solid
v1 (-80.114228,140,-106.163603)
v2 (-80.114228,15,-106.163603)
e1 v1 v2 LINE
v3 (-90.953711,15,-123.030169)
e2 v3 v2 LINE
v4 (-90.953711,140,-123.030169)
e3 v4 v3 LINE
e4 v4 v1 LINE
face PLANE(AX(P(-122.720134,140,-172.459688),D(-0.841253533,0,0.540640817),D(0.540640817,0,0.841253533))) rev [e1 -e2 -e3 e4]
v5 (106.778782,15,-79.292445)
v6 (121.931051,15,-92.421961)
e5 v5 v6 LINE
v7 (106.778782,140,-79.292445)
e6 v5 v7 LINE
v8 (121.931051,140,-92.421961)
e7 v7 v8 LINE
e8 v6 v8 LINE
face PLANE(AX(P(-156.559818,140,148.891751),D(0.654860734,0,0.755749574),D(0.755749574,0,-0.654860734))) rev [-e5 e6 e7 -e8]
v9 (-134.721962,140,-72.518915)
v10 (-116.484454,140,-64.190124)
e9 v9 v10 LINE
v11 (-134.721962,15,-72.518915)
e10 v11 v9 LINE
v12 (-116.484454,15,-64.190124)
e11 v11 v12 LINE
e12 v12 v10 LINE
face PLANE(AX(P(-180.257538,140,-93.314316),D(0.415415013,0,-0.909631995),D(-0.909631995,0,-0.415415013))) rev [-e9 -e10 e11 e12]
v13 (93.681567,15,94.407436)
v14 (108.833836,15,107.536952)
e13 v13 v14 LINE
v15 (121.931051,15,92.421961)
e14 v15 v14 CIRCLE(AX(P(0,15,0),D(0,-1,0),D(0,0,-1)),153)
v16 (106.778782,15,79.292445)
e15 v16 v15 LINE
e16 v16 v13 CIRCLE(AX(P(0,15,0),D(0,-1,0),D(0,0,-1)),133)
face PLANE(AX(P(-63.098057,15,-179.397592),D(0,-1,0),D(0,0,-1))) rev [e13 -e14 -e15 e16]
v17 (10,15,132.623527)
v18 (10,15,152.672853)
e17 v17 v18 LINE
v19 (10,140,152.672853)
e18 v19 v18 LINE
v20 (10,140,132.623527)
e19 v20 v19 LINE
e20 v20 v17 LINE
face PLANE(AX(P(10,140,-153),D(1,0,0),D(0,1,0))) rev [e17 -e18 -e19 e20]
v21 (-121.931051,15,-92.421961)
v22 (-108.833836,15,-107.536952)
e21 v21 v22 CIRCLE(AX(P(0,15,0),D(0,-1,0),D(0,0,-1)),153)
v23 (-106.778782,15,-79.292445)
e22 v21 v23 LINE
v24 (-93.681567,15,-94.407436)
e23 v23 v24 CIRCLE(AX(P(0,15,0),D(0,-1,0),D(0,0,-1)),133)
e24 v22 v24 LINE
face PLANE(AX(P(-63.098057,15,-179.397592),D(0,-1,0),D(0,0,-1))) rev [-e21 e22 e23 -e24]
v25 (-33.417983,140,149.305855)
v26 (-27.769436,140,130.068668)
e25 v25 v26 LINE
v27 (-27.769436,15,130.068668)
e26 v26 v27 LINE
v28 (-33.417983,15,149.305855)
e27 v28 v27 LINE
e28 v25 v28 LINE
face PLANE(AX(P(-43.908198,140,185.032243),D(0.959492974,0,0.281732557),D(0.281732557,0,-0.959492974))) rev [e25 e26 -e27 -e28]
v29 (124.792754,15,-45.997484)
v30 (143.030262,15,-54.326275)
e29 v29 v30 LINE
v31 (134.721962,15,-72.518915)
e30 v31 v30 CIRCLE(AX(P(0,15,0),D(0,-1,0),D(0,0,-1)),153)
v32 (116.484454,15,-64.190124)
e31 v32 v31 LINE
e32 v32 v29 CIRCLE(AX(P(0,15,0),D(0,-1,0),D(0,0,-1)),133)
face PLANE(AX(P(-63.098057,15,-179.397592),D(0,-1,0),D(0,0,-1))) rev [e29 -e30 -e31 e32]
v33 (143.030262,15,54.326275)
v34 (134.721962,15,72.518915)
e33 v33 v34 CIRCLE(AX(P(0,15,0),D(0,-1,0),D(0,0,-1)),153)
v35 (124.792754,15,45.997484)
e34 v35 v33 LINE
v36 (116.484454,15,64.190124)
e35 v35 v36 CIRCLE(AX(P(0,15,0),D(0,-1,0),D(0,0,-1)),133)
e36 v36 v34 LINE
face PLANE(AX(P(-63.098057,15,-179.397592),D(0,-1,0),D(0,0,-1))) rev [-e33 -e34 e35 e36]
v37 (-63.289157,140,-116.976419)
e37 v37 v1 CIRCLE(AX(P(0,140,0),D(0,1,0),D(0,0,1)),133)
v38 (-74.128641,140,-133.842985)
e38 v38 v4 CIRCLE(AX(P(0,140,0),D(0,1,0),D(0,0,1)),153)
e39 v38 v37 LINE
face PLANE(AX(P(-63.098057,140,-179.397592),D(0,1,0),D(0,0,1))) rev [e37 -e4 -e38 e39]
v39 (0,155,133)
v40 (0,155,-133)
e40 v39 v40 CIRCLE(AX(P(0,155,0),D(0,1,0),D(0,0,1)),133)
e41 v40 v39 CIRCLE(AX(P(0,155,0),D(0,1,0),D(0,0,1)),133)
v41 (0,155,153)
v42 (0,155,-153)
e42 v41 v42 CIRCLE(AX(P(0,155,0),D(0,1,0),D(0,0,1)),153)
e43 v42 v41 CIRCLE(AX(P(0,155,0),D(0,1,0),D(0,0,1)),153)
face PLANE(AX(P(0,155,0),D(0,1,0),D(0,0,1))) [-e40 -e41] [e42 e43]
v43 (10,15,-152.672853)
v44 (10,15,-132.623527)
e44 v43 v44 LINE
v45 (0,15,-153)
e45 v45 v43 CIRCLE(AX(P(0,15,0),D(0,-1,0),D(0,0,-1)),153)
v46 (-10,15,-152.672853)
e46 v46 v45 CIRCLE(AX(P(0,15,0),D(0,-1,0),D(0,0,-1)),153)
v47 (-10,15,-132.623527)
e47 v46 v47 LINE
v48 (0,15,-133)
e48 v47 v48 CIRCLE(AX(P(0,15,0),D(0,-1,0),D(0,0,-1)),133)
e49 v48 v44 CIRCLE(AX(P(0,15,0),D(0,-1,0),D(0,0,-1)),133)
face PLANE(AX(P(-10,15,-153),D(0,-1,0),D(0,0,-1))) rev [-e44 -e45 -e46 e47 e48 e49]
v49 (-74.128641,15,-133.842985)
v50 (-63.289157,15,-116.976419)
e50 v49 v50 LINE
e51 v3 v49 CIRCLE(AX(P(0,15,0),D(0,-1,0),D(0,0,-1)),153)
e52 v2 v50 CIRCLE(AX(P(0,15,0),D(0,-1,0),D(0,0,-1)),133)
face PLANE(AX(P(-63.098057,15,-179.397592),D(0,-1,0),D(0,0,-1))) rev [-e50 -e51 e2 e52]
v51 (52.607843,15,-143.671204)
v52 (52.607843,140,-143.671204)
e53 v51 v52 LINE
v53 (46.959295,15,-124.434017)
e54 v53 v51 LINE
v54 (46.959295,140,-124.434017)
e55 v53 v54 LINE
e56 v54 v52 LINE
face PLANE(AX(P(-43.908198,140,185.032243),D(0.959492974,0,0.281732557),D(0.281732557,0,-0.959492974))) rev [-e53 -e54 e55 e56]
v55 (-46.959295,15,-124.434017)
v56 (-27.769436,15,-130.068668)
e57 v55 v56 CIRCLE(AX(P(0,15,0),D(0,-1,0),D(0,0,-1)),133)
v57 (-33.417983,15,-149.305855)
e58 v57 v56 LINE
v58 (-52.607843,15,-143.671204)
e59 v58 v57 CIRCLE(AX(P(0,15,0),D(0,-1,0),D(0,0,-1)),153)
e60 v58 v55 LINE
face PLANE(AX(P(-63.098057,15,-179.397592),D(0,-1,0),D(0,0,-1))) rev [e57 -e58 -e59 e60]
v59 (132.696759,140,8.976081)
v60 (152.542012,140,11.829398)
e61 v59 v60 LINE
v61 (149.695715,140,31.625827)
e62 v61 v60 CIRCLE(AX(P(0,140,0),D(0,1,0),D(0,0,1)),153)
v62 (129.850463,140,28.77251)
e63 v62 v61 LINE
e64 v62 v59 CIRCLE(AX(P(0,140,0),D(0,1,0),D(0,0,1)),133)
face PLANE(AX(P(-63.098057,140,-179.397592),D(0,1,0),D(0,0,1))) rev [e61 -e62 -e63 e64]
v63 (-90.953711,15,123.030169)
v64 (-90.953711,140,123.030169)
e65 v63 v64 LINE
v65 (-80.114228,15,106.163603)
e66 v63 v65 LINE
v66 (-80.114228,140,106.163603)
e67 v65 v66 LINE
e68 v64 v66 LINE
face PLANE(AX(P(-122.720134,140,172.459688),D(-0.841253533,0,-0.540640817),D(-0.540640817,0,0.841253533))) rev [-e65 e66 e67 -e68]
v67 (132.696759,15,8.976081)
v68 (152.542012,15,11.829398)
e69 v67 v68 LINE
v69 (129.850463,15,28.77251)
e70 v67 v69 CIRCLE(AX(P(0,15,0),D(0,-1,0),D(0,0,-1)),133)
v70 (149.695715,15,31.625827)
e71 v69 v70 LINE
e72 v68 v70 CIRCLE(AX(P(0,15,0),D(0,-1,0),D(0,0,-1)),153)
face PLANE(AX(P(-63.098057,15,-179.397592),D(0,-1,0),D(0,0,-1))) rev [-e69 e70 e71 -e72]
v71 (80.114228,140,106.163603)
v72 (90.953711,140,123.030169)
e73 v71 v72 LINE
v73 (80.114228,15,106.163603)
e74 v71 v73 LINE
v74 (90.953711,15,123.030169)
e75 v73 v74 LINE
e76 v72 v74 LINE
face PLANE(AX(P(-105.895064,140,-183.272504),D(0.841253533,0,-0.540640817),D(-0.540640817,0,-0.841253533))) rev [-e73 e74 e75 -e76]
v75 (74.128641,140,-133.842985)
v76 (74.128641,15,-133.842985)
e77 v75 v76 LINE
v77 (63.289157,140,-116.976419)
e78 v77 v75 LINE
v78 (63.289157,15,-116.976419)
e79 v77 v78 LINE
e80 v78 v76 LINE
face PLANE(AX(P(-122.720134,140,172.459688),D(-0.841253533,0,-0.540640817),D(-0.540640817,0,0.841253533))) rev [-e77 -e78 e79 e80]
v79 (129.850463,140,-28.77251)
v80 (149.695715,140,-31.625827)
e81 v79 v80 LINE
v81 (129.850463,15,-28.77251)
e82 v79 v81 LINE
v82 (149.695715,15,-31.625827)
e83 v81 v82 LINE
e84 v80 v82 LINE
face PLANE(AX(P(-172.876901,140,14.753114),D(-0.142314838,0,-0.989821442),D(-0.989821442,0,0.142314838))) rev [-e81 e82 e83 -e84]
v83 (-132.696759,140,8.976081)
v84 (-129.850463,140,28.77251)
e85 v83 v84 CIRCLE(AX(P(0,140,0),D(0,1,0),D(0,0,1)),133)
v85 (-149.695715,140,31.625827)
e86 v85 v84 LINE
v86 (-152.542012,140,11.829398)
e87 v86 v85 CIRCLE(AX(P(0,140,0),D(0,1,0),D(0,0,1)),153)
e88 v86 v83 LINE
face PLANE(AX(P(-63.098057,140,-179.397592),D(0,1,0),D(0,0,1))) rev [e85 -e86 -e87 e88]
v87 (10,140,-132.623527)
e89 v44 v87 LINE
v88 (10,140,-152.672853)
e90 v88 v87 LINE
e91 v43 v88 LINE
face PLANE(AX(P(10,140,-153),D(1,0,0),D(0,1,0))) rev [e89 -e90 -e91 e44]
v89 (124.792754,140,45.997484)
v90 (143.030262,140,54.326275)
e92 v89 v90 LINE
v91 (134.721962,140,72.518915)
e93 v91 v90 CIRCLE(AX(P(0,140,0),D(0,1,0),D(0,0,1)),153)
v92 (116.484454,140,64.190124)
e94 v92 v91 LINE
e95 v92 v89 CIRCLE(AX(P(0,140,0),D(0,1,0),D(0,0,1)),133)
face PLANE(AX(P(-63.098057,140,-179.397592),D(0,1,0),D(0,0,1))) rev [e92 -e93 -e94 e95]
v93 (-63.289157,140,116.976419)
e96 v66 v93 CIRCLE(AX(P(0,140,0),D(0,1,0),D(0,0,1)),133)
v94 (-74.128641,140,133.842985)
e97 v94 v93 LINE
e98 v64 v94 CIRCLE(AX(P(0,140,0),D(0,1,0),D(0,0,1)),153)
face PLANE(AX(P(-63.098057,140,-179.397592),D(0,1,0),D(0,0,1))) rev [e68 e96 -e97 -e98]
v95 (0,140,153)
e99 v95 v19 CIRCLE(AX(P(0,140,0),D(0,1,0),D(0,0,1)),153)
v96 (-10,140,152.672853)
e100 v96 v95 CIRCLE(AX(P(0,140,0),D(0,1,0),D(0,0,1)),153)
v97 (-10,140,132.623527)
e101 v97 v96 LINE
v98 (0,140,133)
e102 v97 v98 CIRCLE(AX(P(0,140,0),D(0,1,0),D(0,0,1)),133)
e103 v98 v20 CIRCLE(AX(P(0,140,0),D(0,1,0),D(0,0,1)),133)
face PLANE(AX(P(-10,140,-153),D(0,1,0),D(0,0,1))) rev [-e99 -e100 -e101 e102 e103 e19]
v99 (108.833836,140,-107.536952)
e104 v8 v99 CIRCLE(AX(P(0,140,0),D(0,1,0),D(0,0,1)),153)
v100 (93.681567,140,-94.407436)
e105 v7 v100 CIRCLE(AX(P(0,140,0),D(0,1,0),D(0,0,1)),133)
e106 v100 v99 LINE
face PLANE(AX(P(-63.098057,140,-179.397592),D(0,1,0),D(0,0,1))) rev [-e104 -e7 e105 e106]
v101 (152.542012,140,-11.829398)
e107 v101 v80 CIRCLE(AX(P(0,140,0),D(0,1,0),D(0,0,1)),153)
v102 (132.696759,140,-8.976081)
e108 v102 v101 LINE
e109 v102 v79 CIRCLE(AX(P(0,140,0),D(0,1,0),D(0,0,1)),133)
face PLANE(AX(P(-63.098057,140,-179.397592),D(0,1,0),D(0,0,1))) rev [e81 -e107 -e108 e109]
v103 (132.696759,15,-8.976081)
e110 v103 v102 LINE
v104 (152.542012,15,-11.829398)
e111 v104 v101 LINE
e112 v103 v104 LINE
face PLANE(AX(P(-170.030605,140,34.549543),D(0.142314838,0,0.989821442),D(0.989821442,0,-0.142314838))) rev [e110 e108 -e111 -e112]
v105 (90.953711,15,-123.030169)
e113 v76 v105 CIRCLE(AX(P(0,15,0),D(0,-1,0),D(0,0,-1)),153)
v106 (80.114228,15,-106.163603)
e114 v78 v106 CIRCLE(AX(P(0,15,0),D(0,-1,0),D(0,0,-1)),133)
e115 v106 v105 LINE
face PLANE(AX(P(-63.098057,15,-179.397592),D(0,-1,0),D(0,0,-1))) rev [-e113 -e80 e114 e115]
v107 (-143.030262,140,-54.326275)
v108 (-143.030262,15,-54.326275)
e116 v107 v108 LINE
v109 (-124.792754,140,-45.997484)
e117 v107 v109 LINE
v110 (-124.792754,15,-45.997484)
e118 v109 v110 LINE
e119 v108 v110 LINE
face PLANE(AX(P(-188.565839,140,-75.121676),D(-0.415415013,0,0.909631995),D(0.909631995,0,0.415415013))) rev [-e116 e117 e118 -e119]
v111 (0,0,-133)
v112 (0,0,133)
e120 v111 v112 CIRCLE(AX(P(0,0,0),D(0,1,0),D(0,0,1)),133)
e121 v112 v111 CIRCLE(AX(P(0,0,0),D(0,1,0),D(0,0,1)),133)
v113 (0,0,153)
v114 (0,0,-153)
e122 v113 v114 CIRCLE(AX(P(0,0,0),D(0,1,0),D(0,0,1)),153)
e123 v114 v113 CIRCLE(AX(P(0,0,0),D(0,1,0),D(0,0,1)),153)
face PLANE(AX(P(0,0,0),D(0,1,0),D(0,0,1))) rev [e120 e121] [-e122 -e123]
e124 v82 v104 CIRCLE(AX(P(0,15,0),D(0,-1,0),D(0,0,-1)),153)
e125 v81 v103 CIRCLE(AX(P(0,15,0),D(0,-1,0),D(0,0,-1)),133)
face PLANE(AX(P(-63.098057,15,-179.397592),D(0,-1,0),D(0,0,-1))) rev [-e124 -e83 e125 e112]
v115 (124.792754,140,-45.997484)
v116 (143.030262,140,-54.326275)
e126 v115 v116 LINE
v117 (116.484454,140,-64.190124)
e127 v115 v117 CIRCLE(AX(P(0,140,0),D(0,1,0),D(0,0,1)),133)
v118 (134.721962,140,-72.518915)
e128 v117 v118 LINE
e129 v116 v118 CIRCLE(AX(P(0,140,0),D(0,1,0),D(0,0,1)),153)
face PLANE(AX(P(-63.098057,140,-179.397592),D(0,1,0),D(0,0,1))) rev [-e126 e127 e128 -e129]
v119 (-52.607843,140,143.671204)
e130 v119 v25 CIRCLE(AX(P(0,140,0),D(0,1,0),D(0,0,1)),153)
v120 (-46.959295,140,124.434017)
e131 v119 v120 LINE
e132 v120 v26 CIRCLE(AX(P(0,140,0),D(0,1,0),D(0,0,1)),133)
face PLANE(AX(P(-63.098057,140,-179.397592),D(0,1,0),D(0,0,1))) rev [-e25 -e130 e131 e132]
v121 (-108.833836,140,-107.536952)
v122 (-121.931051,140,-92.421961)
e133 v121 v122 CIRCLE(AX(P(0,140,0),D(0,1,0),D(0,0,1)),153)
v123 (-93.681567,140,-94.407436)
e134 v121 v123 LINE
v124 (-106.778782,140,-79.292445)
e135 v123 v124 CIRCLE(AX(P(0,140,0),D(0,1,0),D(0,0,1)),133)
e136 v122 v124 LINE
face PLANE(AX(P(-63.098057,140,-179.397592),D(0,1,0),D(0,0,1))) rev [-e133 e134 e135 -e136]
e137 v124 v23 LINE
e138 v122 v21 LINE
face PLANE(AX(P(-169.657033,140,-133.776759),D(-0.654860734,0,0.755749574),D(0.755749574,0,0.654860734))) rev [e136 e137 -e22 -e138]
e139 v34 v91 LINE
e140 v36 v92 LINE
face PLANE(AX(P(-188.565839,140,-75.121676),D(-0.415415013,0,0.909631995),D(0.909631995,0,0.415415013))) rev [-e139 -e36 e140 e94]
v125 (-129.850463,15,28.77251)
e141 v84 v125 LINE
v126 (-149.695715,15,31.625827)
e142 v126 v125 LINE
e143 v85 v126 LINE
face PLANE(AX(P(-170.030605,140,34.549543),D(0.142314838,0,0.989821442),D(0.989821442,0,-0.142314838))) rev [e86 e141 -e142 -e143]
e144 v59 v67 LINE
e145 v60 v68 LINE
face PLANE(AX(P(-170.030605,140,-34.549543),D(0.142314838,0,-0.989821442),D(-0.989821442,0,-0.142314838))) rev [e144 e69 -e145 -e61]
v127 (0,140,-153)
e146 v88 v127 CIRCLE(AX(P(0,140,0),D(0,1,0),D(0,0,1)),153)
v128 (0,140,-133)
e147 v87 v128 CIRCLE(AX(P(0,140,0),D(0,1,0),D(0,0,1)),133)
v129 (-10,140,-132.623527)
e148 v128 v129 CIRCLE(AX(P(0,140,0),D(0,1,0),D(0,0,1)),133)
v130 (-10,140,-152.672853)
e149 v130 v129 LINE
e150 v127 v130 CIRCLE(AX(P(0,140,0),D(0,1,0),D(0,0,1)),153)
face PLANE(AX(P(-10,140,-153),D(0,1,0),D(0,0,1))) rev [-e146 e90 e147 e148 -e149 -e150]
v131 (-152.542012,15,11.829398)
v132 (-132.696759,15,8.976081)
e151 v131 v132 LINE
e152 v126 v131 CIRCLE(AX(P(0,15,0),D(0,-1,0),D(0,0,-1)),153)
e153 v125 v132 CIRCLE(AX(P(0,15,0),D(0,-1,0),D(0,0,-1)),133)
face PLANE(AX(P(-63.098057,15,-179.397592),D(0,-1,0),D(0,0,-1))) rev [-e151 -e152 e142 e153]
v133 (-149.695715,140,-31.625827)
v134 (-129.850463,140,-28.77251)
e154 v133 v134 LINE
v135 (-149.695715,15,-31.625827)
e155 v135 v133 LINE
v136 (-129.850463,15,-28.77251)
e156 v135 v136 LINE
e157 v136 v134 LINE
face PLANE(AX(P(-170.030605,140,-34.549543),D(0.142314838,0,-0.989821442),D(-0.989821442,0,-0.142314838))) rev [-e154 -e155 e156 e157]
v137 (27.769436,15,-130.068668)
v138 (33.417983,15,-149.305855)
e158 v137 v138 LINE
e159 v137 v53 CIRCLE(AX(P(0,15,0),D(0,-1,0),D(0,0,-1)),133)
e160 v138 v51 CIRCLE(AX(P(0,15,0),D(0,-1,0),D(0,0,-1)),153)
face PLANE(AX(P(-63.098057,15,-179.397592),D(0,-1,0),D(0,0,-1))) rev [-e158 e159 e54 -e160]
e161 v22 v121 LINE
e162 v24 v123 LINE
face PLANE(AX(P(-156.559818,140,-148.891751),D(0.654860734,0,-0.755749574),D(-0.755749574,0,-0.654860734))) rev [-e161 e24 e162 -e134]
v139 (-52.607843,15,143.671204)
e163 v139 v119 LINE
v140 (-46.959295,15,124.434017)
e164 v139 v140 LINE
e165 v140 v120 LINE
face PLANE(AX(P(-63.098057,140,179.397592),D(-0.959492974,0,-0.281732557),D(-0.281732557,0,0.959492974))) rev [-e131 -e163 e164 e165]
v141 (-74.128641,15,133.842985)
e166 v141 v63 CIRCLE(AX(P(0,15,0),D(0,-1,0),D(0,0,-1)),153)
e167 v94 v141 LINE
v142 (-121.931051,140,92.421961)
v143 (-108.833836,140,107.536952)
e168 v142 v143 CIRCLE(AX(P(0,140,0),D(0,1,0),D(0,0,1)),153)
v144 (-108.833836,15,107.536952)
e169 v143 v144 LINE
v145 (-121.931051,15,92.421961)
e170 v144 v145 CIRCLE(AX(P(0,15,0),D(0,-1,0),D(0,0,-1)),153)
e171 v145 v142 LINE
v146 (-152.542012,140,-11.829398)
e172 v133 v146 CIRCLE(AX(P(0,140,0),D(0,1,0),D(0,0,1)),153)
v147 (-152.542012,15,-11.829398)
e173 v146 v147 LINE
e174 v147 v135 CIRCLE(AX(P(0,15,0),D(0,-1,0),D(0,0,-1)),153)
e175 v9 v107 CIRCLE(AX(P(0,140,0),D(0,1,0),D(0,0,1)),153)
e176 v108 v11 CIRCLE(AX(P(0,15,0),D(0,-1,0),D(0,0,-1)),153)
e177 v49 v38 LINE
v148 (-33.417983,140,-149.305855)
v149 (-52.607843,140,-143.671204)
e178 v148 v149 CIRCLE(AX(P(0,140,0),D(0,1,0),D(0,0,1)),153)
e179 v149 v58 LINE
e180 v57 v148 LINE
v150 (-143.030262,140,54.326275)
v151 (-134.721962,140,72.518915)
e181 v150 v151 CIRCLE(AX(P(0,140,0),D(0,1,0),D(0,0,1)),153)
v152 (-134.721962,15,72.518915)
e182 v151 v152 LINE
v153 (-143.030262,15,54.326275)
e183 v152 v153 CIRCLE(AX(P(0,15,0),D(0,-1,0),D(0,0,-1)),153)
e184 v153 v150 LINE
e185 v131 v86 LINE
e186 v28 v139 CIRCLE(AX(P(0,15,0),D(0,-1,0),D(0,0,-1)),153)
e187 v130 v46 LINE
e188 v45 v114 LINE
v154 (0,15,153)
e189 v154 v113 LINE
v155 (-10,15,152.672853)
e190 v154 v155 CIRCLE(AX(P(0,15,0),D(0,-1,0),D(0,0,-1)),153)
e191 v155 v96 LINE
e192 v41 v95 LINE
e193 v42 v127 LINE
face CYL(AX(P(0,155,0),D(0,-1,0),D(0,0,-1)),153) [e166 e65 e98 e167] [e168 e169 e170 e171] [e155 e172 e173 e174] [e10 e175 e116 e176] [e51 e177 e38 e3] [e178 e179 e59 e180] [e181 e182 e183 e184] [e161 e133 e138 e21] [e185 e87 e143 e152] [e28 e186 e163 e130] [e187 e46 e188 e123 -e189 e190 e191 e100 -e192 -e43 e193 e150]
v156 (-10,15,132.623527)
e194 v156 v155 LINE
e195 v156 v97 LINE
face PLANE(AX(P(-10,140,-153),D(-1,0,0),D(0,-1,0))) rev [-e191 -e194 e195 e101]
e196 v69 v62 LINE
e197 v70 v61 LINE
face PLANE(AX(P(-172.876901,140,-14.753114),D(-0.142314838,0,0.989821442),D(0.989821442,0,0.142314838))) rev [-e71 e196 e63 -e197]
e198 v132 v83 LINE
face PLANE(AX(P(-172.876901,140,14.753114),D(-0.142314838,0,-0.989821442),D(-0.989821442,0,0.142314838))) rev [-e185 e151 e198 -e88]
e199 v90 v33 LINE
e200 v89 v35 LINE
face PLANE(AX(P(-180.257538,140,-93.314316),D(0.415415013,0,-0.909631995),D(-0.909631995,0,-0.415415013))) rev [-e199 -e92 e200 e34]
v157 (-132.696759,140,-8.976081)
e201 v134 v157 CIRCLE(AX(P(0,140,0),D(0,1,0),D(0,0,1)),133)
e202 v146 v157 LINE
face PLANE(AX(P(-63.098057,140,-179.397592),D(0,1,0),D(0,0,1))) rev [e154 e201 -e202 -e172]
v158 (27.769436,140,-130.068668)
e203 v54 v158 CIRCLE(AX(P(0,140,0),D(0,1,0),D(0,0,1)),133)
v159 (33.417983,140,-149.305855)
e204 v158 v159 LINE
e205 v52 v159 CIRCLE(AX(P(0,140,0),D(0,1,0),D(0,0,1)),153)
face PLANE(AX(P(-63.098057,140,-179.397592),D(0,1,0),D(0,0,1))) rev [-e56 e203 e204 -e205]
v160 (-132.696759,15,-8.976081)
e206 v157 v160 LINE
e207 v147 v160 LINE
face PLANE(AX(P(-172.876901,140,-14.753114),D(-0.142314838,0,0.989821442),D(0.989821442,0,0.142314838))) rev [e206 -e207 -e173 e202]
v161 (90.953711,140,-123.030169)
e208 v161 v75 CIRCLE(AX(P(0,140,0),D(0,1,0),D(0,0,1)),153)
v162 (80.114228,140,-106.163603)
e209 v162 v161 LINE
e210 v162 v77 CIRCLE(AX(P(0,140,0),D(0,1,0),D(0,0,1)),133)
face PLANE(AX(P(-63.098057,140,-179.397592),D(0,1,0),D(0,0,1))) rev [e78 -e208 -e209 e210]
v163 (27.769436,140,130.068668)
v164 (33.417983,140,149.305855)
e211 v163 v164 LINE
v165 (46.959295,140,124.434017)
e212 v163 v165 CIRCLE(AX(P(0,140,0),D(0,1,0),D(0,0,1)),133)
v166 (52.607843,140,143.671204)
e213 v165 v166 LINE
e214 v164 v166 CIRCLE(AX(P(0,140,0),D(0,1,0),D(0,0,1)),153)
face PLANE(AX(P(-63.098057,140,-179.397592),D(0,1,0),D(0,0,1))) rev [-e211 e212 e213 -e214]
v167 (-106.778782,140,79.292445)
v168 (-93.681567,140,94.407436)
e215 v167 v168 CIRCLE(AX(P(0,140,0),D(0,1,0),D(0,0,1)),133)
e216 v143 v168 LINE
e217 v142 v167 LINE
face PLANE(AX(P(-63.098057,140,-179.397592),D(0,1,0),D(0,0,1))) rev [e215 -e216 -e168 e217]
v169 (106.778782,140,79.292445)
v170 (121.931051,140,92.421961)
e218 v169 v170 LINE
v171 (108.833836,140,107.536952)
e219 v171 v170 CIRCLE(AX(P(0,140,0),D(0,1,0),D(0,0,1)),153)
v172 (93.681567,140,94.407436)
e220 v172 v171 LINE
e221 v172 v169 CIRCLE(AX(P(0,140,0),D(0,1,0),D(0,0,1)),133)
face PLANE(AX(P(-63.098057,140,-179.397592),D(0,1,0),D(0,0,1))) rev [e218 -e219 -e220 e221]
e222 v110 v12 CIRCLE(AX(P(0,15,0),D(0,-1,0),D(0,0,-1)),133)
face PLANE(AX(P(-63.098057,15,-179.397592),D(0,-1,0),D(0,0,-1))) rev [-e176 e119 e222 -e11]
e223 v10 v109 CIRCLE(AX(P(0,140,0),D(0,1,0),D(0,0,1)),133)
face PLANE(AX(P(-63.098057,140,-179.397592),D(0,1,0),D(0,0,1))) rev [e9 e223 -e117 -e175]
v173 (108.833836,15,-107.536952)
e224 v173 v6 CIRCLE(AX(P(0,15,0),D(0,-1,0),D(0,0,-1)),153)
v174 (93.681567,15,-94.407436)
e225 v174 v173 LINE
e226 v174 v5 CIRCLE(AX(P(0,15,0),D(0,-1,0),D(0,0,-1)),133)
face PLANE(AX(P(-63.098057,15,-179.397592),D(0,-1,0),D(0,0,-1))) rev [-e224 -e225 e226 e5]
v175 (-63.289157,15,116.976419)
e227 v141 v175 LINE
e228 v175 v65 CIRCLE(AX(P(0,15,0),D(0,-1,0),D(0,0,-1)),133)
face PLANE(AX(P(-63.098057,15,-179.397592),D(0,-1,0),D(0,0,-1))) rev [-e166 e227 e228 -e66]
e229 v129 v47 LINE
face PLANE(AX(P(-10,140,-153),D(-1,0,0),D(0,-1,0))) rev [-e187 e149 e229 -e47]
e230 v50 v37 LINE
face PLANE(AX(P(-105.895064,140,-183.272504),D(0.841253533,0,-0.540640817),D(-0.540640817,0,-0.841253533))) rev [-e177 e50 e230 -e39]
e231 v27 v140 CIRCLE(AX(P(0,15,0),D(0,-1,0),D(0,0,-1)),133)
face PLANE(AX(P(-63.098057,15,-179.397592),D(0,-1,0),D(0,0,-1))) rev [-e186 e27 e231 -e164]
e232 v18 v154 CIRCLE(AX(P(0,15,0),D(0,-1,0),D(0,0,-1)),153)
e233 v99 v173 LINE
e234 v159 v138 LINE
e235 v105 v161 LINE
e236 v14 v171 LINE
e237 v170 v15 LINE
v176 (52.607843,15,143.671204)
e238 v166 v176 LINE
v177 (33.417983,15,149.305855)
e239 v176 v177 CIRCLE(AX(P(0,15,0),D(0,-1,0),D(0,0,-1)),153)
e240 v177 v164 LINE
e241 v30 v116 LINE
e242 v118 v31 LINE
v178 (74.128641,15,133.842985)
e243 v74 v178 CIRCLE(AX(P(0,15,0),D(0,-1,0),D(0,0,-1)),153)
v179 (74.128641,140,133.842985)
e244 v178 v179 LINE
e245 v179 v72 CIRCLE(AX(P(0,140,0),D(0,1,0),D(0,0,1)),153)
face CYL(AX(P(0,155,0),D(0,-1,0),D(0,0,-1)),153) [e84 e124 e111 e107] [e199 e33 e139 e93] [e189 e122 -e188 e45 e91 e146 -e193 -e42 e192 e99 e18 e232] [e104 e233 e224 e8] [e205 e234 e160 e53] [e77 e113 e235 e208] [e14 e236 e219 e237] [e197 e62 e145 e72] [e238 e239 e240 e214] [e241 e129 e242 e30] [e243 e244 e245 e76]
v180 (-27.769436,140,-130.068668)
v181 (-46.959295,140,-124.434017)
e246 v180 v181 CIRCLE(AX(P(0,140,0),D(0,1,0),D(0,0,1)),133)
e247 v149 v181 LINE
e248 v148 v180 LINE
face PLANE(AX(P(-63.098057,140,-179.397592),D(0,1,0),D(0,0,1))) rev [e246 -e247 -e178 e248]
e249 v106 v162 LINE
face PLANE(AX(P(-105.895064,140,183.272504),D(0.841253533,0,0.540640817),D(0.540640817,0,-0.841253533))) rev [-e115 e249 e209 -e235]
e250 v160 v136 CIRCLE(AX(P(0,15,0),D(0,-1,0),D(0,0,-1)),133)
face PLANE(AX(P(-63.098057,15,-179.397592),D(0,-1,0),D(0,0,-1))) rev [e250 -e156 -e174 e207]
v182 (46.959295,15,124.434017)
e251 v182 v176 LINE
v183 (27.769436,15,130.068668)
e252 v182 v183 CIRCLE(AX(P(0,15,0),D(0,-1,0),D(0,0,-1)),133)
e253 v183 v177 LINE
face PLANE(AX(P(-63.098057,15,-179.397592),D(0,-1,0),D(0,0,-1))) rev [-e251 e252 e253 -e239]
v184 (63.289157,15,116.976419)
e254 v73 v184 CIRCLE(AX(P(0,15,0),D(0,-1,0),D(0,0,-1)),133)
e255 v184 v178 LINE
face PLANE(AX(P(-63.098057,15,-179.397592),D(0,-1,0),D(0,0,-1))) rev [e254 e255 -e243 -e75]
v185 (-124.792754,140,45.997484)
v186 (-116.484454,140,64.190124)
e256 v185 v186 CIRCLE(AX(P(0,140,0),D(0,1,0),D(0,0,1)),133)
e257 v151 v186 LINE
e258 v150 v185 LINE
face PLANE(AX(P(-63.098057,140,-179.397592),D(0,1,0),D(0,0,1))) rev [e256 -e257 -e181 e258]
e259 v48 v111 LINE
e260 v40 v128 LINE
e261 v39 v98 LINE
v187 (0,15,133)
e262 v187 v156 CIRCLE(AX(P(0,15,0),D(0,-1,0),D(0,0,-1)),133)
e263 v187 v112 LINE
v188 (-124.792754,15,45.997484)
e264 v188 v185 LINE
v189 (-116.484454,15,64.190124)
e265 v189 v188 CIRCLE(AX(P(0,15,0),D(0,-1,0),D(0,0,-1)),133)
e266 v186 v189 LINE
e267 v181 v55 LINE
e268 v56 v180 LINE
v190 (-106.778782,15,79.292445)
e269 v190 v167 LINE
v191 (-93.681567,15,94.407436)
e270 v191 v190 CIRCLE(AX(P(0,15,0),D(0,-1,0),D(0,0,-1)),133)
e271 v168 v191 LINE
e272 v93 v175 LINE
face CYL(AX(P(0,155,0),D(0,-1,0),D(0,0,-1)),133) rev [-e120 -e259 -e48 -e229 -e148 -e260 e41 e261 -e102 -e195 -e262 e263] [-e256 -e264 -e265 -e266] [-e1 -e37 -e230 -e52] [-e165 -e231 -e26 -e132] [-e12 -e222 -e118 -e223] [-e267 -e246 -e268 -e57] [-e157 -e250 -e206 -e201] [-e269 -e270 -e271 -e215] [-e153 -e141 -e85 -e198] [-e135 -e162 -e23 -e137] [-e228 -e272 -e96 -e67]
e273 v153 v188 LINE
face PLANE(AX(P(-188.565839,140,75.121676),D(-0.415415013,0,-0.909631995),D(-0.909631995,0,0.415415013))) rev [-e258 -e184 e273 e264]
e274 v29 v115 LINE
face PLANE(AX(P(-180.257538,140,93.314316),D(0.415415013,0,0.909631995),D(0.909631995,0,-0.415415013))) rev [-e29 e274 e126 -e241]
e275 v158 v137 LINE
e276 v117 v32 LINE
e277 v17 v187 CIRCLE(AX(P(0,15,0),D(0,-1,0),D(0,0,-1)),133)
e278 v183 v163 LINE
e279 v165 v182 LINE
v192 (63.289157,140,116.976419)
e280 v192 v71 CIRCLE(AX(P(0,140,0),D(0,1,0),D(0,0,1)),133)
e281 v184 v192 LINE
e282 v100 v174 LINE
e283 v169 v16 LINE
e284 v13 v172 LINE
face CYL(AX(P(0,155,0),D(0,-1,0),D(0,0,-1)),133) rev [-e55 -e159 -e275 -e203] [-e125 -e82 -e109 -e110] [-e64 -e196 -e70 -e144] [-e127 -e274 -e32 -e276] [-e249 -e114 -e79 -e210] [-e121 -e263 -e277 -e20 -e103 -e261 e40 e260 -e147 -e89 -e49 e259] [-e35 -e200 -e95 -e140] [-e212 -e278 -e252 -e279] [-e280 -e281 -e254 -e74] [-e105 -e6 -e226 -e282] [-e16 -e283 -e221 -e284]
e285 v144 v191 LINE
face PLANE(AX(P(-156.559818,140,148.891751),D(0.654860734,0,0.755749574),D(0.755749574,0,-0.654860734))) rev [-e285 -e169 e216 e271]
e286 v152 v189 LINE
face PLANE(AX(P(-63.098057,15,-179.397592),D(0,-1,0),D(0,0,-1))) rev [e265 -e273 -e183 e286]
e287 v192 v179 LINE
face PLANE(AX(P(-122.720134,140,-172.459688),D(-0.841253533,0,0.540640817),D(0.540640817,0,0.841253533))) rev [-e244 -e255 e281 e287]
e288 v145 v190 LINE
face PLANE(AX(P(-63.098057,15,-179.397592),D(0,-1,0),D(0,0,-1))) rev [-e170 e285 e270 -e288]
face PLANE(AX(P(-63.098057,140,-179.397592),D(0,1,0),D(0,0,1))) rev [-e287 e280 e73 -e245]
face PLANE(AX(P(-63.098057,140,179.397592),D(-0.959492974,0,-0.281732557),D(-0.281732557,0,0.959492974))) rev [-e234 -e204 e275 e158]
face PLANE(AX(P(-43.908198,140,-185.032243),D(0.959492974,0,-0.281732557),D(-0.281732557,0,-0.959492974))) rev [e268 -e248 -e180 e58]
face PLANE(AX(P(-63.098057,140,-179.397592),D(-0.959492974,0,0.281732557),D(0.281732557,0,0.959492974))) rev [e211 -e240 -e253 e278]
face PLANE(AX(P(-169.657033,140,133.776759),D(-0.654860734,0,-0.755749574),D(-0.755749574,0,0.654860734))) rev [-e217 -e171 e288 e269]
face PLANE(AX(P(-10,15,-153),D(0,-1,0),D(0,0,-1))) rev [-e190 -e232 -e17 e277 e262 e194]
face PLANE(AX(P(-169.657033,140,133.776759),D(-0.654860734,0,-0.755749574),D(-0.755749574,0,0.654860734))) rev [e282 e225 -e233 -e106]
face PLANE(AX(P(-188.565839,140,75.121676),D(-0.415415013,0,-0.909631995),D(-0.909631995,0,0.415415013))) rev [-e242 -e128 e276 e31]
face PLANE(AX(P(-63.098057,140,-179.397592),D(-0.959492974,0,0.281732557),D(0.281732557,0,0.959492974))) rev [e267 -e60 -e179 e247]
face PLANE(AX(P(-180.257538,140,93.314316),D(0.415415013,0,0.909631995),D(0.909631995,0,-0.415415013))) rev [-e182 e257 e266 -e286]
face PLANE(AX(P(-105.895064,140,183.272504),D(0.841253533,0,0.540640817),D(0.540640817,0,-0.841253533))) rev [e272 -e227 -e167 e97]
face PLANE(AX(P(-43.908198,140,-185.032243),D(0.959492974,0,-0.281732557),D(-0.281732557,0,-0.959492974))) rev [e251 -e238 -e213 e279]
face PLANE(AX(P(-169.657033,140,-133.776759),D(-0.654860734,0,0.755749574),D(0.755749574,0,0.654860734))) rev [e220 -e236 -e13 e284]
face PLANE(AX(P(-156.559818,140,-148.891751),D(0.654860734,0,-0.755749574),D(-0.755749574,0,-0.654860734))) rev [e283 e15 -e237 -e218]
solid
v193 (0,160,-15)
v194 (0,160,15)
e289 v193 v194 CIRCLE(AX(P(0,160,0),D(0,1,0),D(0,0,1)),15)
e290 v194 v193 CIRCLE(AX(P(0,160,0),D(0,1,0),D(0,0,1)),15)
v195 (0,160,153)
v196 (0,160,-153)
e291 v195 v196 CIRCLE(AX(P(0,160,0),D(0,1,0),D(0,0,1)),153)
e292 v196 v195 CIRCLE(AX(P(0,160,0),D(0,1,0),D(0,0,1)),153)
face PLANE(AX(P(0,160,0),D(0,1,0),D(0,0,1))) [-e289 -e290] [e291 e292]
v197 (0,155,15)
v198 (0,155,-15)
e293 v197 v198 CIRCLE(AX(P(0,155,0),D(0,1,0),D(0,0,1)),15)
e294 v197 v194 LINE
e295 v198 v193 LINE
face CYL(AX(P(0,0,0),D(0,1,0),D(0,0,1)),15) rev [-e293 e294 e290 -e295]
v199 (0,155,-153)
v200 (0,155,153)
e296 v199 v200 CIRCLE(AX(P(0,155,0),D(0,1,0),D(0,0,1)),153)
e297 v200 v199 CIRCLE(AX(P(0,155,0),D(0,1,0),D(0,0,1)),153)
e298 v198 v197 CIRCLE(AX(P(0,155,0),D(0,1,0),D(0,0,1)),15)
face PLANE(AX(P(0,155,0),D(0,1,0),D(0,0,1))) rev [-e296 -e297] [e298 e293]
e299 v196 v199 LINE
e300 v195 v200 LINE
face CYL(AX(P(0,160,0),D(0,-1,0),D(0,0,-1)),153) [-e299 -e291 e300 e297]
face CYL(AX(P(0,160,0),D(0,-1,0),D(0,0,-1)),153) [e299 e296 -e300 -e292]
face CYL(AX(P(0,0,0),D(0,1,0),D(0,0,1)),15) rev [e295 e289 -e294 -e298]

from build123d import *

# Parameters (mm, degrees)
SKETCH1_R           = 153
SKETCH1_R_2         = 133
BOSS_EXTRUDE1_DEPTH = 155
SKETCH2_W           = 20
SKETCH2_H           = 125
CUT_EXTRUDE1_DEPTH  = 267.163483596
CIRPATTERN1_COUNT   = 22
SKETCH3_R           = 153
BOSS_EXTRUDE2_DEPTH = 5
SKETCH4_R           = 15
CUT_EXTRUDE2_DEPTH  = 270.105927099


with BuildPart() as part:
    # Sketch1 → Boss-Extrude1 (new body)
    with BuildSketch(Plane(origin=(0, 0, 0), x_dir=(1, 0, 0), z_dir=(0, 1, 0))):
        with Locations(Location((0, 0, 0), (0, 0, 270))):
            Circle(SKETCH1_R)
        with Locations(Location((0, 0, 0), (0, 0, 270))):
            Circle(SKETCH1_R_2, mode=Mode.SUBTRACT)
    extrude(amount=BOSS_EXTRUDE1_DEPTH)

    # Sketch2 → Cut-Extrude1 (cut, symmetric)
    with BuildSketch(Plane.XY):
        with Locations((0, 77.5)):
            Rectangle(SKETCH2_W, SKETCH2_H)
    cut_extrude1 = extrude(amount=CUT_EXTRUDE1_DEPTH, both=True, mode=Mode.SUBTRACT)

    # CirPattern1: Cut-Extrude1 ×22 about axis
    cirpattern1_axis = Axis((0, 0, 0), (0, 1, 0))
    for i in range(1, CIRPATTERN1_COUNT):
        add(cut_extrude1.rotate(cirpattern1_axis, i * 360 / CIRPATTERN1_COUNT), mode=Mode.SUBTRACT)


with BuildPart() as body_2:
    # Sketch3 → Boss-Extrude2 (new body)
    with BuildSketch(Plane(origin=(0, 155, 0), x_dir=(1, 0, 0), z_dir=(0, 1, 0))):
        with Locations(Location((0, 0, 0), (0, 0, 270))):
            Circle(SKETCH3_R)
    extrude(amount=BOSS_EXTRUDE2_DEPTH)

    # Sketch4 → Cut-Extrude2 (cut, through all)
    with BuildSketch(Plane(origin=(0, 160, 0), x_dir=(1, 0, 0), z_dir=(0, 1, 0))):
        with Locations(Location((0, 0, 0), (0, 0, 270))):
            Circle(SKETCH4_R)
    extrude(amount=-CUT_EXTRUDE2_DEPTH, mode=Mode.SUBTRACT)


solid = Compound([part.part, body_2.part])
